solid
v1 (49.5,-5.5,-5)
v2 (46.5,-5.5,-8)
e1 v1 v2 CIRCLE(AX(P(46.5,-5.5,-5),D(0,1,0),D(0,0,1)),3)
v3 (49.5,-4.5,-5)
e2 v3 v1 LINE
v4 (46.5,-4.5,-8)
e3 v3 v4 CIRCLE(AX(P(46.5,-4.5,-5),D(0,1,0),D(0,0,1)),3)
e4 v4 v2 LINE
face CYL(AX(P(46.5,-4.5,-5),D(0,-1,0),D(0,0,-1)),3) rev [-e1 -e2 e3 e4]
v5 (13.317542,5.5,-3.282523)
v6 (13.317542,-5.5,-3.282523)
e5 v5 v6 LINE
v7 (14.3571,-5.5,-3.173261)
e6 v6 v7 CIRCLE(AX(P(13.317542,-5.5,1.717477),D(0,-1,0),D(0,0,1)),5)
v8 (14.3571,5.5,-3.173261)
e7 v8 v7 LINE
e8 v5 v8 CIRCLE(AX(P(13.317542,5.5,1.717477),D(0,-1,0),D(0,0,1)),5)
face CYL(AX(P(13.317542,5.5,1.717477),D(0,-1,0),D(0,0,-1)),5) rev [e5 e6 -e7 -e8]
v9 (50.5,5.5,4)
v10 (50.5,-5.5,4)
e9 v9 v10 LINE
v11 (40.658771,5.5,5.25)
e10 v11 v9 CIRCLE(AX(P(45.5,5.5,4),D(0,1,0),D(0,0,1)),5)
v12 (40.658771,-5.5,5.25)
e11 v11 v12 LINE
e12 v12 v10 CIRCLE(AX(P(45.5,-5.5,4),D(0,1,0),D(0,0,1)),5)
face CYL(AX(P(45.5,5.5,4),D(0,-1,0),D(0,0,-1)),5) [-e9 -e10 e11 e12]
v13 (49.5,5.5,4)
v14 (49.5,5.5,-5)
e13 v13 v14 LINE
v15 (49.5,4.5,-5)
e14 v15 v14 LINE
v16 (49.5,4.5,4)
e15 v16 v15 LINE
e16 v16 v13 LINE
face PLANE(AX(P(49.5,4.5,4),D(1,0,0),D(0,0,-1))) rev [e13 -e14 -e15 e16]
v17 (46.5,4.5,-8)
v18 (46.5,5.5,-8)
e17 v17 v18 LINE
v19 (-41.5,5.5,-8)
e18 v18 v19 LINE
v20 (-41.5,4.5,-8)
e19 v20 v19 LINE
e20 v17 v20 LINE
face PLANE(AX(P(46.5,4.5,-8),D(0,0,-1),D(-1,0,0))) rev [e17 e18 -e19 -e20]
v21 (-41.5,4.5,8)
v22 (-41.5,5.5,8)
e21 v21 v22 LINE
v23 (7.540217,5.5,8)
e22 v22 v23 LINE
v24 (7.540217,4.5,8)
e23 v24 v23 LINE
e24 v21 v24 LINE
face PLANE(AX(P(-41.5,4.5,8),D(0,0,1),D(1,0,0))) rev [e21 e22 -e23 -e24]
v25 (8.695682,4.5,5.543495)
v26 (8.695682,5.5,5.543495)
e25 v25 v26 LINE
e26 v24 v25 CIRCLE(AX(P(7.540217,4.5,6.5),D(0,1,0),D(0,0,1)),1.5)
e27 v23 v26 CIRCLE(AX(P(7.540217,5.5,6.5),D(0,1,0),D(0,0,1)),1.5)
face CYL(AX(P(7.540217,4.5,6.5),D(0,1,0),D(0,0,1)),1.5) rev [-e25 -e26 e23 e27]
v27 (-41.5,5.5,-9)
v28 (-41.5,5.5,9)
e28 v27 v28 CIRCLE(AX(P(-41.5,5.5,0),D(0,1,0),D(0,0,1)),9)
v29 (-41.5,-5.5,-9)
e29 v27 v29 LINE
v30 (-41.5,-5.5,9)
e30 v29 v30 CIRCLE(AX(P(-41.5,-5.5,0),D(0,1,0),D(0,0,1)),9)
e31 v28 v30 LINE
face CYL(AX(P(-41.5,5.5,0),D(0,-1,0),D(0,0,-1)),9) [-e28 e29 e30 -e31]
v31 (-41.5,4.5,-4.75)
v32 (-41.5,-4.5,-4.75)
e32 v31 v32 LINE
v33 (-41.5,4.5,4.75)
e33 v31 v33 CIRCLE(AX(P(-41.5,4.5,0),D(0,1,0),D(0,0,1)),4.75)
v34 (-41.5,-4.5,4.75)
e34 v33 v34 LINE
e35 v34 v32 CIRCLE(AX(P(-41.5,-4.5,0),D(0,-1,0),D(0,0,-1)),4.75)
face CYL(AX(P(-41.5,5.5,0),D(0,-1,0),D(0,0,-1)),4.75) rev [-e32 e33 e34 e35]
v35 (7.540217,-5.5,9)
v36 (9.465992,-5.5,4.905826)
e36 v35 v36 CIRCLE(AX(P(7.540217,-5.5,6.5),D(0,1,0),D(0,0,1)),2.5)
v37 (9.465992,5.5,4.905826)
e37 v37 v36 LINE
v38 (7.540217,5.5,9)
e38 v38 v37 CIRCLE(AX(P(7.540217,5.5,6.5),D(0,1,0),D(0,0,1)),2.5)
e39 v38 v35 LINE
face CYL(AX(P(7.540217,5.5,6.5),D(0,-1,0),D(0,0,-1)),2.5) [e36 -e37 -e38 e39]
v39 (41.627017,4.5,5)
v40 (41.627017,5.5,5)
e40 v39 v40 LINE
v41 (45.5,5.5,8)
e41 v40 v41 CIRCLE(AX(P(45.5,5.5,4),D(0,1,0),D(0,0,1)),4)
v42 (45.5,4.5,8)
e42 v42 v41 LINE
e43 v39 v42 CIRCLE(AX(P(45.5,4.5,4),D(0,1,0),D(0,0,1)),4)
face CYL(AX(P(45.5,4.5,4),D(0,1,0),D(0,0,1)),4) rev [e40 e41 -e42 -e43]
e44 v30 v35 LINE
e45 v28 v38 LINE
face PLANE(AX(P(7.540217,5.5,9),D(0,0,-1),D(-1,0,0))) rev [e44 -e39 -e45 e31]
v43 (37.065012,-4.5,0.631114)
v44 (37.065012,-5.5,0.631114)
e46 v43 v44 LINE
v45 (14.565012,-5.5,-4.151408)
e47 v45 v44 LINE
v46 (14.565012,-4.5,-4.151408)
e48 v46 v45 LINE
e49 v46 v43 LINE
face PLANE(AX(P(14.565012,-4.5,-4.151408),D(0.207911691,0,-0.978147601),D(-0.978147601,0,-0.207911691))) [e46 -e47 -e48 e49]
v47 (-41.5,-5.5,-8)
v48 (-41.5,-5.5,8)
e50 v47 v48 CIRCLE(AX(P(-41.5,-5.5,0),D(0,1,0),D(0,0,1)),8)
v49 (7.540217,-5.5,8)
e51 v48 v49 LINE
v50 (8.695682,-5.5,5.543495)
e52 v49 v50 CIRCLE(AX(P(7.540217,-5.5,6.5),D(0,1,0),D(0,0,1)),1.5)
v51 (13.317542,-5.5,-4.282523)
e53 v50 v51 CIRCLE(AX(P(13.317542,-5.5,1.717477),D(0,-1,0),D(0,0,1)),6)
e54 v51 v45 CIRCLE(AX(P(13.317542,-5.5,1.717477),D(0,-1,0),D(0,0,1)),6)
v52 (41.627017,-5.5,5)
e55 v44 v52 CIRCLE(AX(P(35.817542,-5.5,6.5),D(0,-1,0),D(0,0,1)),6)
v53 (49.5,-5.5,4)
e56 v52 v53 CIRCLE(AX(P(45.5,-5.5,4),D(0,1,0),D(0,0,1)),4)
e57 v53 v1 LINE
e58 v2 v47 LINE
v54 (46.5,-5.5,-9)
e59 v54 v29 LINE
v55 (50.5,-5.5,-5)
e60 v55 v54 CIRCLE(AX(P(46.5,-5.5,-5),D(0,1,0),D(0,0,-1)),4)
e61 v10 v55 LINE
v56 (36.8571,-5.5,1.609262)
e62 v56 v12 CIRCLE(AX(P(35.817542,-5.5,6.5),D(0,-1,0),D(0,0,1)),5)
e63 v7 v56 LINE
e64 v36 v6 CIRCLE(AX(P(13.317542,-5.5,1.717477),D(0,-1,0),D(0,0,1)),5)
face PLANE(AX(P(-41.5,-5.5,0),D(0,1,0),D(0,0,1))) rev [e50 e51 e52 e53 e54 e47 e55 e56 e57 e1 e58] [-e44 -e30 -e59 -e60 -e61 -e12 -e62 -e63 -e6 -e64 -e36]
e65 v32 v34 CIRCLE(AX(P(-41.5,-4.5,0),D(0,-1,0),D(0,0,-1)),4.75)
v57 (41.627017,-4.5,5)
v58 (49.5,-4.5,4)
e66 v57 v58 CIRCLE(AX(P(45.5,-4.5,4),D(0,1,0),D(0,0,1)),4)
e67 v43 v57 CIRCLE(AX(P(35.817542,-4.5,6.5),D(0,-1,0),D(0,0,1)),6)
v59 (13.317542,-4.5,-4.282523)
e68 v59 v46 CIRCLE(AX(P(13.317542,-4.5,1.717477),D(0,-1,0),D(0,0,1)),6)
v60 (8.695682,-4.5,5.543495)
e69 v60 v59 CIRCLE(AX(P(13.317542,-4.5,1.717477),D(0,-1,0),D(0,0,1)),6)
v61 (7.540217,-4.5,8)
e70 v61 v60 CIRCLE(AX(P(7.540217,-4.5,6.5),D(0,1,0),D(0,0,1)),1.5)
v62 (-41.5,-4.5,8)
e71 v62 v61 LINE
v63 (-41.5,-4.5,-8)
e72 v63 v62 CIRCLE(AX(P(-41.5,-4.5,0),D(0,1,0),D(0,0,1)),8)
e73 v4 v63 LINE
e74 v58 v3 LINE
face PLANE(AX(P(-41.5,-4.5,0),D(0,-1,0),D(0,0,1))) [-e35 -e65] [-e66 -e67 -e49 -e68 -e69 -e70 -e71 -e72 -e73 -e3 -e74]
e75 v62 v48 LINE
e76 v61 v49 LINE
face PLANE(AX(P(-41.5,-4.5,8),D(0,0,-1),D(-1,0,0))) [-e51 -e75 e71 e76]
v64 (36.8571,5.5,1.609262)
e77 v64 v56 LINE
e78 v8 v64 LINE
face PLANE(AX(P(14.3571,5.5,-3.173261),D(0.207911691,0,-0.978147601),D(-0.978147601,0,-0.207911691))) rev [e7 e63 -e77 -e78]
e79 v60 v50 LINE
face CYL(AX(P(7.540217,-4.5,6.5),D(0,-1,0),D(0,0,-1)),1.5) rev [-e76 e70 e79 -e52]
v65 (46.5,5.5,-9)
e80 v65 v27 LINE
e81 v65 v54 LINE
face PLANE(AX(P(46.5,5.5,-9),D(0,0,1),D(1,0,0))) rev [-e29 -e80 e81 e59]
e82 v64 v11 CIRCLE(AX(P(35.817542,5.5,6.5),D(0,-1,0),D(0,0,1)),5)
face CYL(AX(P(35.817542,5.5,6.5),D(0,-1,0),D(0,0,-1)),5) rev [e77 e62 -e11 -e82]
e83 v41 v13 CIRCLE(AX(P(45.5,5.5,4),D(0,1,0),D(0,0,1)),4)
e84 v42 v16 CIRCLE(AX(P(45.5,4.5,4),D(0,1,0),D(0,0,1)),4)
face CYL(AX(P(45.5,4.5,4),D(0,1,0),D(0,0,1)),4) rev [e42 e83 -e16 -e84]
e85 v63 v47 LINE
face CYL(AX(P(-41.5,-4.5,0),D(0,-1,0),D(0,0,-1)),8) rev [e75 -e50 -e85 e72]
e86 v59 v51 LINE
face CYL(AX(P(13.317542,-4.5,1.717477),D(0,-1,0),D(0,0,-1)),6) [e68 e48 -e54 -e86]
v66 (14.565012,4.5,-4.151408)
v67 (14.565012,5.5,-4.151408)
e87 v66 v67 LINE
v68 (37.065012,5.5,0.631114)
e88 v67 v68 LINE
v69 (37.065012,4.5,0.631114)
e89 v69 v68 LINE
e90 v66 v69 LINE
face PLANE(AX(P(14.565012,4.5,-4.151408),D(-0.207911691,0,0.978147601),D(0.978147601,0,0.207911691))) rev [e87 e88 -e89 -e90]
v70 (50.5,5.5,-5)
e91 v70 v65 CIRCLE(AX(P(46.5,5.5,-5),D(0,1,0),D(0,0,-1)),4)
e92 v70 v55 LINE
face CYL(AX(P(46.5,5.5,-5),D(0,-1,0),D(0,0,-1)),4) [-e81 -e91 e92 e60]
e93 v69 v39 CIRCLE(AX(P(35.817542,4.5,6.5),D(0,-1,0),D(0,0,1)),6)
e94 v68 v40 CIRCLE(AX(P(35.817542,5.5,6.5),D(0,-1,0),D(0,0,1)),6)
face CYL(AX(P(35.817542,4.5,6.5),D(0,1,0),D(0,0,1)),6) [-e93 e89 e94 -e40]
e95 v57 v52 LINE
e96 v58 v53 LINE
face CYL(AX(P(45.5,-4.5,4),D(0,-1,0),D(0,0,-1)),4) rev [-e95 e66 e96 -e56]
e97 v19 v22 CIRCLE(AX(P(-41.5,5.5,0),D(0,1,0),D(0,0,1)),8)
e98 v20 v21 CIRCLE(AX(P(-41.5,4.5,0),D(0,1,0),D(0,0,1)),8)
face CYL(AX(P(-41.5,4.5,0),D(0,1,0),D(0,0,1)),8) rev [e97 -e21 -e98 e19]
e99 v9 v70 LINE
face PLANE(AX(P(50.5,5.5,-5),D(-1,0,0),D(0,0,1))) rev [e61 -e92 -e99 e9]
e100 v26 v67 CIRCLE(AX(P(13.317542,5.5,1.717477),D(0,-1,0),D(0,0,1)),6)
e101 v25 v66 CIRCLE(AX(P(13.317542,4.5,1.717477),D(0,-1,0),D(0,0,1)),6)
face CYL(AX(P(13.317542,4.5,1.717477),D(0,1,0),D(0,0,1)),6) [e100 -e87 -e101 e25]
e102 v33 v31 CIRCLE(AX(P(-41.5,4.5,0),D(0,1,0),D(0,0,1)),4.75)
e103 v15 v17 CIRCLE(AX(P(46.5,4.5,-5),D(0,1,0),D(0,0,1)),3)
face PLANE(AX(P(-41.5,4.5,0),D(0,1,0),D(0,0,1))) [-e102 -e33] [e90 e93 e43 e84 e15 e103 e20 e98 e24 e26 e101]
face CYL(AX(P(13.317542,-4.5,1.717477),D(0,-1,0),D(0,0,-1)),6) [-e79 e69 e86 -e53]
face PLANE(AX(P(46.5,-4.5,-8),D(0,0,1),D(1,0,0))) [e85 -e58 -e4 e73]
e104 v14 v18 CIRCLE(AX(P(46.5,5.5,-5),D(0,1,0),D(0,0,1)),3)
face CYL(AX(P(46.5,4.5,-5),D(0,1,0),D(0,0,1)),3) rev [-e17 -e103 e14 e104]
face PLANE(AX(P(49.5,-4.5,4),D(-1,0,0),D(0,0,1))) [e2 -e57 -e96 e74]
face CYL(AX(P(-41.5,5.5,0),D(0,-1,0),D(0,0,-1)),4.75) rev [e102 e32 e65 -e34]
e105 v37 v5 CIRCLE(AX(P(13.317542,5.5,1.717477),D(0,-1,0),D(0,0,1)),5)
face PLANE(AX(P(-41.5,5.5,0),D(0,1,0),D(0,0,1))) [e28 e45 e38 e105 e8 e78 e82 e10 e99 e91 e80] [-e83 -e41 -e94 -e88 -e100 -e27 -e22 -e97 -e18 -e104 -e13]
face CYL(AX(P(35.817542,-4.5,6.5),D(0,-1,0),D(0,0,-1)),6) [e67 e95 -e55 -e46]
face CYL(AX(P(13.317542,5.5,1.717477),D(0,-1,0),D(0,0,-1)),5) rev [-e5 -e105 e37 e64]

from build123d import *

# Parameters (mm, degrees)
LEVER_PROFILE_SKETCH_R    = 4.75
LEVER_BODY_11MM_DEPTH     = 5.5
TOP_FACE_RECESS_1MM_DEPTH = 1


with BuildPart() as part:
    # Lever Profile Sketch → Lever Body 11mm (new, symmetric)
    with BuildSketch(Plane(origin=(0, 0, 0), x_dir=(1, 0, 0), z_dir=(0, 1, 0))):
        with BuildLine():
            Line((46.5, 9), (-41.5, 9))
            ThreePointArc((-41.5, 9), (-50.5, 0), (-41.5, -9))
            Line((-41.5, -9), (7.540217235, -9))
            ThreePointArc((7.540217235, -9), (9.802454571, -7.564087513), (9.465992035, -4.905825787))
            ThreePointArc((9.465992035, -4.905825787), (9.040307373, 0.871975682), (14.357100089, 3.173260641))
            Line((14.357100089, 3.173260641), (36.857100089, -1.609261996))
            ThreePointArc((36.857100089, -1.609261996), (39.275815642, -2.888858783), (40.658770817, -5.25))
            ThreePointArc((40.658770817, -5.25), (46.130021462, -8.960148481), (50.5, -4))
            Line((50.5, -4), (50.5, 5))
            ThreePointArc((50.5, 5), (49.328427125, 7.828427125), (46.5, 9))
        make_face()
        with Locations(Location((-41.5, 0, 0), (0, 0, 270))):
            Circle(LEVER_PROFILE_SKETCH_R, mode=Mode.SUBTRACT)
    extrude(amount=LEVER_BODY_11MM_DEPTH, both=True)

    # Face Recess Sketch → Top Face Recess 1mm (cut)
    with BuildSketch(Plane(origin=(0, 5.5, 0), x_dir=(1, 0, 0), z_dir=(0, 1, 0))):
        with BuildLine():
            Line((-41.5, -8), (7.540217235, -8))
            ThreePointArc((7.540217235, -8), (8.897559636, -7.138452508), (8.695682115, -5.543495472))
            ThreePointArc((8.695682115, -5.543495472), (8.18486052, 1.389866291), (14.565011779, 4.151408242))
            Line((14.565011779, 4.151408242), (37.065011779, -0.631114396))
            ThreePointArc((37.065011779, -0.631114396), (39.967470443, -2.166630539), (41.627016654, -5))
            ThreePointArc((41.627016654, -5), (46.00401717, -7.968118785), (49.5, -4))
            Line((49.5, -4), (49.5, 5))
            ThreePointArc((49.5, 5), (48.621320344, 7.121320344), (46.5, 8))
            Line((46.5, 8), (-41.5, 8))
            ThreePointArc((-41.5, 8), (-49.5, 0), (-41.5, -8))
        make_face()
    top_face_recess_1mm = extrude(amount=-TOP_FACE_RECESS_1MM_DEPTH, mode=Mode.SUBTRACT)

    # Bottom Face Recess Mirror: Top Face Recess 1mm across plane
    add(top_face_recess_1mm.mirror(Plane.ZX), mode=Mode.SUBTRACT)


solid = part.part
